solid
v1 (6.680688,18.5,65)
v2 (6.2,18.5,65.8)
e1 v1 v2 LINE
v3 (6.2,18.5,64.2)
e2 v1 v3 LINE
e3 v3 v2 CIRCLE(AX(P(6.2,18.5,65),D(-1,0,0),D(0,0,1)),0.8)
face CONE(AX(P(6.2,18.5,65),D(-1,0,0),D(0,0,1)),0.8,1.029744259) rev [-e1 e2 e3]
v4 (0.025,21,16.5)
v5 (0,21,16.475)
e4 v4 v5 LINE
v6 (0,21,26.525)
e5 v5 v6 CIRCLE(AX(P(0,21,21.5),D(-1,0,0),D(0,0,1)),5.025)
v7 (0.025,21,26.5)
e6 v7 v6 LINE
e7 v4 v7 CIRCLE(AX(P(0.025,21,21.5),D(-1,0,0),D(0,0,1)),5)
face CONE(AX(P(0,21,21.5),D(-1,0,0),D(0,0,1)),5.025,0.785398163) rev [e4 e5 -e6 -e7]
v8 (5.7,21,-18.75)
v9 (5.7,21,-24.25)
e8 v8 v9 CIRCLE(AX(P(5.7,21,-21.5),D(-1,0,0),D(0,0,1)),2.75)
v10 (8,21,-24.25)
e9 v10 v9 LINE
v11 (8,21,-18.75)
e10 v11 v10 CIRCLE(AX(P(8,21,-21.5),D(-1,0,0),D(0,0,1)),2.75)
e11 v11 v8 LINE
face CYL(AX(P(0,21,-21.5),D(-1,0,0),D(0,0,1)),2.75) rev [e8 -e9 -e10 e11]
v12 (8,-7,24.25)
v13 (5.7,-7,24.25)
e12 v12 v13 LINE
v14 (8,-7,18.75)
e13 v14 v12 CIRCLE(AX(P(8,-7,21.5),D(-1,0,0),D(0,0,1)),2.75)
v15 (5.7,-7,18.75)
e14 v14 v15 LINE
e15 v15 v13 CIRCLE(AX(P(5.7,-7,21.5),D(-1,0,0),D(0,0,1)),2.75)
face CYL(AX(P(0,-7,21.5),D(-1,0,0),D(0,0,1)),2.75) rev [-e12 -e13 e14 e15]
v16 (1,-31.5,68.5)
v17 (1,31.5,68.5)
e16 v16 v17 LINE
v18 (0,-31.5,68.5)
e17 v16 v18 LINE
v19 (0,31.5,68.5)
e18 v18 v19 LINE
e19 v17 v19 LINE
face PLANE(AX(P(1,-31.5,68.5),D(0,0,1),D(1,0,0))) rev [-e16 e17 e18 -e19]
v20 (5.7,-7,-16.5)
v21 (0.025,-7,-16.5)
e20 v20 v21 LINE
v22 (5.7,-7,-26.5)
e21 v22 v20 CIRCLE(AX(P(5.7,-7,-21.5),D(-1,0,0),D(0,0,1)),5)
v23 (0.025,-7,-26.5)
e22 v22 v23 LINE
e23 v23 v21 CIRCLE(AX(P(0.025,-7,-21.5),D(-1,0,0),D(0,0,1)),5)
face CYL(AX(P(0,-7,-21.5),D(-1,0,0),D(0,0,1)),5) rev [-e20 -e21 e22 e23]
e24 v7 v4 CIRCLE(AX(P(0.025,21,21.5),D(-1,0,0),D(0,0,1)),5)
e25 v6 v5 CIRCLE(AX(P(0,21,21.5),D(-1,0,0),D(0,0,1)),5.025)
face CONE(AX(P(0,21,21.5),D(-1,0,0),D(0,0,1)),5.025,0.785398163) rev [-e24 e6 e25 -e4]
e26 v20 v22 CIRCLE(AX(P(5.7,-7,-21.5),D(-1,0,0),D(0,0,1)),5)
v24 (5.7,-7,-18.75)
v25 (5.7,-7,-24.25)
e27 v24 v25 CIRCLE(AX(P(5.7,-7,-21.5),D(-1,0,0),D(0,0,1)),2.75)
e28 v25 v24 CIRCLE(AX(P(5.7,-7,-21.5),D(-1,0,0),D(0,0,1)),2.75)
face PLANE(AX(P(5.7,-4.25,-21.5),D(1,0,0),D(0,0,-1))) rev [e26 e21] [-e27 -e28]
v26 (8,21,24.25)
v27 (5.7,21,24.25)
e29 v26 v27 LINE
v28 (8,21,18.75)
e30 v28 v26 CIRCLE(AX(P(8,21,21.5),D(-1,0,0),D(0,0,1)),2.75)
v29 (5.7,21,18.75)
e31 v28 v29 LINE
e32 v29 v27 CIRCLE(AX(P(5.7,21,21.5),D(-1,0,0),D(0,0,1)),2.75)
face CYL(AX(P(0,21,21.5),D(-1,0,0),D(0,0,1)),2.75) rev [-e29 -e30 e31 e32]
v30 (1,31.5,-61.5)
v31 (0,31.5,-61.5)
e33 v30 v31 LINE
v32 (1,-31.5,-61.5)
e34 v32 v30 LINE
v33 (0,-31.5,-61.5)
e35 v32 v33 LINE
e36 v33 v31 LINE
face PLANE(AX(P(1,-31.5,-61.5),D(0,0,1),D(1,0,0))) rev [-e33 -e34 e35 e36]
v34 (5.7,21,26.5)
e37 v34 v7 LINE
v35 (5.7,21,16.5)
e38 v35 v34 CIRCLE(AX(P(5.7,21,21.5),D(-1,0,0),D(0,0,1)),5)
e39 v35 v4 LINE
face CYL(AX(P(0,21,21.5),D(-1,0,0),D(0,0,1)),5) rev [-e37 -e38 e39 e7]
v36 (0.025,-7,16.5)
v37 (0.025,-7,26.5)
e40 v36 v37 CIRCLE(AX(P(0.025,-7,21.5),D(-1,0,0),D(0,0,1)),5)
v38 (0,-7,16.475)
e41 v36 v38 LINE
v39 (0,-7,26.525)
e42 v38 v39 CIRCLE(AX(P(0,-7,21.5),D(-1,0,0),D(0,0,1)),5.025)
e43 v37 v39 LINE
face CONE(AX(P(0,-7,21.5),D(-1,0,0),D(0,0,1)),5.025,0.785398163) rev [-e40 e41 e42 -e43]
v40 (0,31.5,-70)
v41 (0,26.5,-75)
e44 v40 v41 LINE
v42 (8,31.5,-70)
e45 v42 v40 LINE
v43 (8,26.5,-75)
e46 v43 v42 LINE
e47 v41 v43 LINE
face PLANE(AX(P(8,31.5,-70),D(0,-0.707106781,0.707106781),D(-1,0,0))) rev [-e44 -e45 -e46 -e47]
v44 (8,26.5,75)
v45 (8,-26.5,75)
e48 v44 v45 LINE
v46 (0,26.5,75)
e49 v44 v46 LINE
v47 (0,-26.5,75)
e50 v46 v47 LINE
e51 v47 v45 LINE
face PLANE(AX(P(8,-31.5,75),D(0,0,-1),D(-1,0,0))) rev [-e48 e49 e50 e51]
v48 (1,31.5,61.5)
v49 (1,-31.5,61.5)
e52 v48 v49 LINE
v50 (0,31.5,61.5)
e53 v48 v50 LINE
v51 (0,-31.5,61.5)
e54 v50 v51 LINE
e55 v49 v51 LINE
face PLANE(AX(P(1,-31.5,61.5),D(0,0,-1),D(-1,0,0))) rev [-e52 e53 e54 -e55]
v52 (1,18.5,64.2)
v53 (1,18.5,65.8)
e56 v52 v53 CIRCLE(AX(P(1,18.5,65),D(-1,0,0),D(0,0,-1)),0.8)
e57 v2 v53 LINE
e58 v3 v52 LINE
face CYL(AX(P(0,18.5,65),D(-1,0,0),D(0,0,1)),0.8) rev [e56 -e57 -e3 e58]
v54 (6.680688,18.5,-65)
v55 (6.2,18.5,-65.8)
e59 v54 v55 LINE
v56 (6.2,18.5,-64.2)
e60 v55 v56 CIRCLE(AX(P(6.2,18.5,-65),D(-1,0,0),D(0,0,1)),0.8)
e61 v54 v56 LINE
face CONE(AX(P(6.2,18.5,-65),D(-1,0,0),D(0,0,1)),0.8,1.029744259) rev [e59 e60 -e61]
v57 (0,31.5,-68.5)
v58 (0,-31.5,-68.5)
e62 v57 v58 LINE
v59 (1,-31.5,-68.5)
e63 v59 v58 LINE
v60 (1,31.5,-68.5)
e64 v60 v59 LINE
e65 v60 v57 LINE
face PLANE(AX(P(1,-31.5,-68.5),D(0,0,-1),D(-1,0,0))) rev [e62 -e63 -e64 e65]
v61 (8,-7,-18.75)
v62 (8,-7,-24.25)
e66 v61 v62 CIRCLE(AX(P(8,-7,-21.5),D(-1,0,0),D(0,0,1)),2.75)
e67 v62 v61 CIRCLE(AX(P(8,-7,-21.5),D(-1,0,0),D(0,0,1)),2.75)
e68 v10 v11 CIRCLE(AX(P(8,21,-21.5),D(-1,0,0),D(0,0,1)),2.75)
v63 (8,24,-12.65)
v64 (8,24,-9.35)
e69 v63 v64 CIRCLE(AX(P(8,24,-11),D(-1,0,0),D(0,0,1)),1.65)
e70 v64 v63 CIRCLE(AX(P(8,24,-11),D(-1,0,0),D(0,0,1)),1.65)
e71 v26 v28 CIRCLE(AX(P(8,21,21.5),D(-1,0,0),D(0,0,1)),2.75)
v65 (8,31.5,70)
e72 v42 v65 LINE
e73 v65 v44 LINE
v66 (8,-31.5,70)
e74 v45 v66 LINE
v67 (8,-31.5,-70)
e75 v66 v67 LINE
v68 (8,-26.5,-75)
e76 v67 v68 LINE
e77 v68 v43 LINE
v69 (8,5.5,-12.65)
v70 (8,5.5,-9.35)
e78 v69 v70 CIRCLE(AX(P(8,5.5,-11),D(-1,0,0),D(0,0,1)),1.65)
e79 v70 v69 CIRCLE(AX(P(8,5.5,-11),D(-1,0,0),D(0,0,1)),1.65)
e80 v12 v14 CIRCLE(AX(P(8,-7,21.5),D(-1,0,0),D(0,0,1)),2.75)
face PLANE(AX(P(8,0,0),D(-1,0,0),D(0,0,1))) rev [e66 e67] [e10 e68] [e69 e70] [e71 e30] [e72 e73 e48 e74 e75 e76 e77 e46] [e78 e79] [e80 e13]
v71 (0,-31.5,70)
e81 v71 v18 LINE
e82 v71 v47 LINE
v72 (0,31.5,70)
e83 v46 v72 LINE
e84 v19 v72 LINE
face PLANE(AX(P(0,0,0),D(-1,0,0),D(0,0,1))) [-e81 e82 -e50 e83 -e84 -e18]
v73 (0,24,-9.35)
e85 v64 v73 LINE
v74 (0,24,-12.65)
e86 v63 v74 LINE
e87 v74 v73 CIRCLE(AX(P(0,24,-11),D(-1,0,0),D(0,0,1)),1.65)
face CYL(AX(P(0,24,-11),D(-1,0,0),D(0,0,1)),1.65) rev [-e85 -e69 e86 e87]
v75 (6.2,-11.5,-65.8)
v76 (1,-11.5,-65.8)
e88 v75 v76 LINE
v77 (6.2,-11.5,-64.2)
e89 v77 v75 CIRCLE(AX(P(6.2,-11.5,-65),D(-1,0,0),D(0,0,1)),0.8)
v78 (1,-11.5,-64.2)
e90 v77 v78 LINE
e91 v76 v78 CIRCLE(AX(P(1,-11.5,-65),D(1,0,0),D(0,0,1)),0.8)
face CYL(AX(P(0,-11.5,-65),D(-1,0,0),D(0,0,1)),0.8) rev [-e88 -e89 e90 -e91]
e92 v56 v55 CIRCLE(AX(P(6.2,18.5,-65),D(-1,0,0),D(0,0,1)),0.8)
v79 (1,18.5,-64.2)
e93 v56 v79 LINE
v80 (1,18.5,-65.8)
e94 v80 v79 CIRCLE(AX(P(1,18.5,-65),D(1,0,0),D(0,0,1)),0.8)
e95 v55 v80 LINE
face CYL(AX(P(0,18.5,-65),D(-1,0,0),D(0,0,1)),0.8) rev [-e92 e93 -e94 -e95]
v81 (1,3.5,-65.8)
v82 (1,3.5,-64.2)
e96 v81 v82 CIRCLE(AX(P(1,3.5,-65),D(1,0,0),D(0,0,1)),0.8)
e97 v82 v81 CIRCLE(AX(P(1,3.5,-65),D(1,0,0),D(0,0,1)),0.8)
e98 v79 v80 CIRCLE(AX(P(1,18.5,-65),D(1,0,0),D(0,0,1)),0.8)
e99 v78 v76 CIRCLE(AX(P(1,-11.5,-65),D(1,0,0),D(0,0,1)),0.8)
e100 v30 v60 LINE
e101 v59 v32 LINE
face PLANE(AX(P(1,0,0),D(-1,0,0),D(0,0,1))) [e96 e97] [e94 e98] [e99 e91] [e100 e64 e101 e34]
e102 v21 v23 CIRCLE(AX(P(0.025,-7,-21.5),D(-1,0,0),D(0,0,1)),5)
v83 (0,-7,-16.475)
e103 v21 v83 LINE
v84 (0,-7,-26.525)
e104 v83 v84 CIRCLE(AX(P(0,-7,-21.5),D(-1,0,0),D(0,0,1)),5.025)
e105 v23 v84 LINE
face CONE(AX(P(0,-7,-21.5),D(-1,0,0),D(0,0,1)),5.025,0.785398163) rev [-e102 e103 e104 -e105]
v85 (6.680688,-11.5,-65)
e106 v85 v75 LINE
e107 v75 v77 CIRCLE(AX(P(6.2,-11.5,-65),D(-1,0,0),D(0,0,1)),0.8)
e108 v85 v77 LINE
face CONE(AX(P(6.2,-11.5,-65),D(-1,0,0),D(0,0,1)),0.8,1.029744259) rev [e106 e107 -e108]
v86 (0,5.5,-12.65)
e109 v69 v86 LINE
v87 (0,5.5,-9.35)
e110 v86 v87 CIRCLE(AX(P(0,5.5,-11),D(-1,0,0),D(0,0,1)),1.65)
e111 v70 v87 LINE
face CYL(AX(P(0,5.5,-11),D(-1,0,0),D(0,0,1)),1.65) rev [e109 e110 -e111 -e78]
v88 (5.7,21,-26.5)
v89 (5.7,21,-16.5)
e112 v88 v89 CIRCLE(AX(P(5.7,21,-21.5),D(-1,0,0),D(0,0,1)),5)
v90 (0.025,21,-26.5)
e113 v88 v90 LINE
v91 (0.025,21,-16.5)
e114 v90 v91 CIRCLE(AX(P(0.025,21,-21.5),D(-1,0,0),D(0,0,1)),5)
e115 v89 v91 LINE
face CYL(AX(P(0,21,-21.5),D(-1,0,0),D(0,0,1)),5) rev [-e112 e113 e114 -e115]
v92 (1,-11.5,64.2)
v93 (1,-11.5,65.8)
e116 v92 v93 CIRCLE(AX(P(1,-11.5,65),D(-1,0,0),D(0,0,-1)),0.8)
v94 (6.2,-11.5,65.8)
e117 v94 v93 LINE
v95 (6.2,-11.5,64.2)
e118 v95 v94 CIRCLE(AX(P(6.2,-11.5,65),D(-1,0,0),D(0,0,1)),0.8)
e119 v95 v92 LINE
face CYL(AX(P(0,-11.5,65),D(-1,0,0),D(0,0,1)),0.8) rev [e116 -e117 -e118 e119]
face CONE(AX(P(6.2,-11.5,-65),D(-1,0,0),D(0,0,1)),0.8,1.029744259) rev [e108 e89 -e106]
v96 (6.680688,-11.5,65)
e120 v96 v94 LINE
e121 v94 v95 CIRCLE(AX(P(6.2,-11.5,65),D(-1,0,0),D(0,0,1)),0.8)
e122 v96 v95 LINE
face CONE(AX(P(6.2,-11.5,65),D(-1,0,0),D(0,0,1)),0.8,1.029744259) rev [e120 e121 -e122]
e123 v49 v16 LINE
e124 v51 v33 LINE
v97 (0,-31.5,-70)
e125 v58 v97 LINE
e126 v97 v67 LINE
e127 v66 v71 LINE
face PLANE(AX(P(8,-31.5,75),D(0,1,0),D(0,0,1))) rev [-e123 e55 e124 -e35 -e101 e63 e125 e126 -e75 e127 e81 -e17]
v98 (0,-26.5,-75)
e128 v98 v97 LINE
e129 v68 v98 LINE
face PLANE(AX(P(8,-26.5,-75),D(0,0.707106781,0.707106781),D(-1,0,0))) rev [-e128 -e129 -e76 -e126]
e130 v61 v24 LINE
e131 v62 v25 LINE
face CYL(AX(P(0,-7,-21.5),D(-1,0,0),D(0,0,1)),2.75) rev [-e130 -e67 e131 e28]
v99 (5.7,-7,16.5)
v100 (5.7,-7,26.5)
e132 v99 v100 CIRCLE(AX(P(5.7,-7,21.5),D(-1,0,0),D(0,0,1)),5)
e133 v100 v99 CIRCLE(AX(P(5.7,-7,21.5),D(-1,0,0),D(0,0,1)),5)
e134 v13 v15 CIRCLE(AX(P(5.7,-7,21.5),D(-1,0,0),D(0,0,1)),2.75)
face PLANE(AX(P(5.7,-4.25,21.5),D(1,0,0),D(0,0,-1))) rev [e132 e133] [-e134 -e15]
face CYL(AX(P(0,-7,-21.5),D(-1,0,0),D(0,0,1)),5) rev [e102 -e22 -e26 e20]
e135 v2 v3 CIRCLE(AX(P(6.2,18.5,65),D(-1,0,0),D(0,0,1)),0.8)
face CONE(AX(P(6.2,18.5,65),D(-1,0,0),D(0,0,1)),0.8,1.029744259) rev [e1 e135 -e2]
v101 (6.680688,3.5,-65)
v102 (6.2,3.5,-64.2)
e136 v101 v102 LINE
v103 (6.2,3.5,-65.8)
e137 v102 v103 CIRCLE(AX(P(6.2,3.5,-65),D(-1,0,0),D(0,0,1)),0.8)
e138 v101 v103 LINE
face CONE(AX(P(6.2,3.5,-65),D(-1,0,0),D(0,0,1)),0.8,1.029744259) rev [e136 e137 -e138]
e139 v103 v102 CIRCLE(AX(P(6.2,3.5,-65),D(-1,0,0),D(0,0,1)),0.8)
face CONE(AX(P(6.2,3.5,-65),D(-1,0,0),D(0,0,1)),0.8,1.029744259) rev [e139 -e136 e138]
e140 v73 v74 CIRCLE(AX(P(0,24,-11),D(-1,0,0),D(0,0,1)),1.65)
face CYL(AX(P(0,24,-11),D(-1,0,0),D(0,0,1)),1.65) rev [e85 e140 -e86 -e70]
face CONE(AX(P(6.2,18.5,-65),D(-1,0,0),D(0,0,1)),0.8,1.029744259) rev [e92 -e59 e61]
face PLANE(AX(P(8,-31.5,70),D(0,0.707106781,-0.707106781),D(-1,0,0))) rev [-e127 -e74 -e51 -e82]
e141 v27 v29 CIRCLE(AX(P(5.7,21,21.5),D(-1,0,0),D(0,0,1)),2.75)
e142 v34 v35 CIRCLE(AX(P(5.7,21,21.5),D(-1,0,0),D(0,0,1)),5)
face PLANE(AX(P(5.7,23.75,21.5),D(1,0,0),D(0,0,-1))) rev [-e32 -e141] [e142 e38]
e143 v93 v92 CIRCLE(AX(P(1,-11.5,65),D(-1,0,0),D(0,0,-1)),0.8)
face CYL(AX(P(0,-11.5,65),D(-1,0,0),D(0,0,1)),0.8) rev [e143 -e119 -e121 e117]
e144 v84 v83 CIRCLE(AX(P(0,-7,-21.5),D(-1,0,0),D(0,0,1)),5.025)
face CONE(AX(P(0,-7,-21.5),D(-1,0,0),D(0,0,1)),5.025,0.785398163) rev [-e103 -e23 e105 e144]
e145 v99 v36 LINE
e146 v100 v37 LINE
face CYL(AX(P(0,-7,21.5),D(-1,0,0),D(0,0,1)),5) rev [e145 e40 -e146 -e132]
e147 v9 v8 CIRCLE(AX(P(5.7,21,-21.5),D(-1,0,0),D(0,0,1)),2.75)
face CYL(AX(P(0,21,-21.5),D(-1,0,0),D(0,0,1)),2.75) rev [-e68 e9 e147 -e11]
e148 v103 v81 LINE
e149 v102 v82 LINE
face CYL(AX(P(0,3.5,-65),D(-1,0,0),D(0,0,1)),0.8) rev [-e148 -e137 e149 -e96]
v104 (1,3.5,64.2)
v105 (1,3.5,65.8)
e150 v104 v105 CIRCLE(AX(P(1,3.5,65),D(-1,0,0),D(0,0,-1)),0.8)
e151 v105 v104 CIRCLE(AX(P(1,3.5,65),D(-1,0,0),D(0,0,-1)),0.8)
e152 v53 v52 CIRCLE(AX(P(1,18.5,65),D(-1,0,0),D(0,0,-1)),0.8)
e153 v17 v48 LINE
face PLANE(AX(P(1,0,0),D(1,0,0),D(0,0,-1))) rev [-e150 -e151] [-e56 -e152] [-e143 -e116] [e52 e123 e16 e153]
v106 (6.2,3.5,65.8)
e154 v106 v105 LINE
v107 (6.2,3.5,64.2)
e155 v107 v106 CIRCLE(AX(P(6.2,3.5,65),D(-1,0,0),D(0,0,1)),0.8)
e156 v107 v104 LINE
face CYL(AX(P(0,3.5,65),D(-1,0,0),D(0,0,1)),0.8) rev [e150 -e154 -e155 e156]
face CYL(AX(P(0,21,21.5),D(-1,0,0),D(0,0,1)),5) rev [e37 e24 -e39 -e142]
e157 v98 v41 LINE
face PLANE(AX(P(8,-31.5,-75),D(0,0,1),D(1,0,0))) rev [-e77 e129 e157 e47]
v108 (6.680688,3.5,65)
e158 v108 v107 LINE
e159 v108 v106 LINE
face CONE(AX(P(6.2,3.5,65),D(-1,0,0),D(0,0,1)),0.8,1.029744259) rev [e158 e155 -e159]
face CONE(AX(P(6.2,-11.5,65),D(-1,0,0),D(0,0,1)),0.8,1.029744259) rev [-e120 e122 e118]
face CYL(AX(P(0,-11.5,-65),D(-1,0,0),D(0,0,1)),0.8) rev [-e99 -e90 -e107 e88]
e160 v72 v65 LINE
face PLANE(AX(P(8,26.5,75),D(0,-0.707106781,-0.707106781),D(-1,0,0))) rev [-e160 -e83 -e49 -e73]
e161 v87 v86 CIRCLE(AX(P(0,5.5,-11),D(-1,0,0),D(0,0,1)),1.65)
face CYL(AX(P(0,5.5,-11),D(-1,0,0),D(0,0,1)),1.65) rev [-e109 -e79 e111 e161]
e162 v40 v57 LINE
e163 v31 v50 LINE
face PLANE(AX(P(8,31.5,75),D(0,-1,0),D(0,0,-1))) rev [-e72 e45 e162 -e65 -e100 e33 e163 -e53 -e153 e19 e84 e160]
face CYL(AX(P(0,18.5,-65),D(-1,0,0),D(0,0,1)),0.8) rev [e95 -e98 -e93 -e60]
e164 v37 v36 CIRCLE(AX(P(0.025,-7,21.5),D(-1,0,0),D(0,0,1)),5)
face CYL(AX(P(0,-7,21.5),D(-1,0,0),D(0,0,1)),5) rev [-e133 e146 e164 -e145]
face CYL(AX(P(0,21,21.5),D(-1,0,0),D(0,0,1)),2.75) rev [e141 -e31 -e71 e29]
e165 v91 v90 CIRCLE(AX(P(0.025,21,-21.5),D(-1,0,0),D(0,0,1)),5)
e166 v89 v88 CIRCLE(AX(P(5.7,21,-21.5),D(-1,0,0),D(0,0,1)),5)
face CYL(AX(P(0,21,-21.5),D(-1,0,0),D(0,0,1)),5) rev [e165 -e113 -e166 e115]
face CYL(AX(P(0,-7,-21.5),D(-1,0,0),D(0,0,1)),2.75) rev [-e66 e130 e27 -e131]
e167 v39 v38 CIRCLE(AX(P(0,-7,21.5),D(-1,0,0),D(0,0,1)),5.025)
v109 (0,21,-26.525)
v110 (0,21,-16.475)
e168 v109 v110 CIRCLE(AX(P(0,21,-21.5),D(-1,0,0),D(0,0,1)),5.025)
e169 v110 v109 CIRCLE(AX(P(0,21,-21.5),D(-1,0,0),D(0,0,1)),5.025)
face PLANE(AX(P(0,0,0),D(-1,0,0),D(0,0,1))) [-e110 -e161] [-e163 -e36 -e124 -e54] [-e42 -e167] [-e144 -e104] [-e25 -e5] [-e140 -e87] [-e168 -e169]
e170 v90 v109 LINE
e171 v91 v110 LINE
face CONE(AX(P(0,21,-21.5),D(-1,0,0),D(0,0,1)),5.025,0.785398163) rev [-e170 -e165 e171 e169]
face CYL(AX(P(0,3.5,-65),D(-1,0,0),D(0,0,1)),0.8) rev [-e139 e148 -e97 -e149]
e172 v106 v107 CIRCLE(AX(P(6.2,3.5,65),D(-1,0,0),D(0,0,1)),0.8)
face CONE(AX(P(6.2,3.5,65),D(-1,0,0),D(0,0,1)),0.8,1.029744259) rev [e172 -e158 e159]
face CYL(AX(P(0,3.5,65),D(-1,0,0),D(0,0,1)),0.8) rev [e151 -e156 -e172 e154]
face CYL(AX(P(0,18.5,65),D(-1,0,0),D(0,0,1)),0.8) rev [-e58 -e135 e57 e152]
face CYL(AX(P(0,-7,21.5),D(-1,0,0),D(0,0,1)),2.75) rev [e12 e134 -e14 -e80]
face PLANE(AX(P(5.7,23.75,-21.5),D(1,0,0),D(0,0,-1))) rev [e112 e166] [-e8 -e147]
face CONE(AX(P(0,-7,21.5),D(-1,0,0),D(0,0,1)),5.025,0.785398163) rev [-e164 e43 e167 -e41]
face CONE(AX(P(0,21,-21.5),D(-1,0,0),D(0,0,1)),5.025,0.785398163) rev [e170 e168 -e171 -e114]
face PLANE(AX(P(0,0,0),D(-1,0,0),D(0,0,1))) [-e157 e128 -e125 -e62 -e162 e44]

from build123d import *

# Parameters (mm, degrees)
SKETCH1_W                                    = 150
SKETCH1_H                                    = 63
BOSS_EXTRUDE1_DEPTH                          = 8
M4_TAPPED_HOLE1_D                            = 3.3
M4_TAPPED_HOLE1_DEPTH                        = 10.1
M4_TAPPED_HOLE1_TIP                          = 0.991420021
CBORE_FOR_M5_HEXAGON_SOCKET_HEAD_CAP_2_COUNT = 2
CBORE_FOR_M5_HEXAGON_SOCKET_HEAD_CAP_2_PITCH = 28
CBORE_FOR_M5_HEXAGON_SOCKET_HEAD_CAP_3_COUNT = 2
CBORE_FOR_M5_HEXAGON_SOCKET_HEAD_CAP_3_PITCH = 43
CBORE_FOR_M5_HEXAGON_SOCKET_HEAD_CAP_4_COUNT = 2
CBORE_FOR_M5_HEXAGON_SOCKET_HEAD_CAP_4_PITCH = 51.312766443
M2_TAPPED_HOLE1_D                            = 1.6
M2_TAPPED_HOLE1_DEPTH                        = 6.2
M2_TAPPED_HOLE1_TIP                          = 0.480688495
SKETCH17_W                                   = 7
SKETCH17_H                                   = 63
CUT_EXTRUDE1_DEPTH                           = 1
CHAMFER1_SIZE                                = 5


with BuildPart() as part:
    # Sketch1 → Boss-Extrude1 (new body)
    with BuildSketch(Plane(origin=(0, 0, 0), x_dir=(0, 0, -1), z_dir=(1, 0, 0))):
        Rectangle(SKETCH1_W, SKETCH1_H)
    extrude(amount=BOSS_EXTRUDE1_DEPTH)

    # M4 Tapped Hole1
    with Locations(Plane.ZY):
        with Locations((-11, 24), (-11, 5.5)):
            Hole(M4_TAPPED_HOLE1_D / 2, depth=M4_TAPPED_HOLE1_DEPTH)
            with Locations((0, 0, -(M4_TAPPED_HOLE1_DEPTH + M4_TAPPED_HOLE1_TIP / 2))):  # 118° drill point
                Cone(0, M4_TAPPED_HOLE1_D / 2, M4_TAPPED_HOLE1_TIP, mode=Mode.SUBTRACT)

    # Sketch15 → CBORE for M5 Hexagon socket head cap screws1 (revolve, cut)
    with BuildSketch(Plane(origin=(0, 21, 21.5), x_dir=(0, 0, 1), z_dir=(0, 1, 0))):
        Polygon((0, 0), (0, 14.052366702), (2.75, 12.4), (2.75, 5.7), (5, 5.7), (5, 0.025), (5.025, 0), align=None)
    cbore_for_m5_hexagon_socket_head_cap_scr = revolve(axis=Axis((-6.35, 21, 21.5), (1, 0, 0)), mode=Mode.SUBTRACT)

    # CBORE for M5 Hexagon socket head cap 2: CBORE for M5 Hexagon socket head cap screws1 ×2
    with Locations(*[(0, -i * CBORE_FOR_M5_HEXAGON_SOCKET_HEAD_CAP_2_PITCH, 0) for i in range(1, CBORE_FOR_M5_HEXAGON_SOCKET_HEAD_CAP_2_COUNT)]):
        add(cbore_for_m5_hexagon_socket_head_cap_scr, mode=Mode.SUBTRACT)

    # CBORE for M5 Hexagon socket head cap 3: CBORE for M5 Hexagon socket head cap screws1 ×2
    with Locations(*[(0, 0, -i * CBORE_FOR_M5_HEXAGON_SOCKET_HEAD_CAP_3_PITCH) for i in range(1, CBORE_FOR_M5_HEXAGON_SOCKET_HEAD_CAP_3_COUNT)]):
        add(cbore_for_m5_hexagon_socket_head_cap_scr, mode=Mode.SUBTRACT)

    # CBORE for M5 Hexagon socket head cap 4: CBORE for M5 Hexagon socket head cap screws1 ×2
    with Locations(*[Vector(0, -0.5456731714374324, -0.8379980847074858) * (i * CBORE_FOR_M5_HEXAGON_SOCKET_HEAD_CAP_4_PITCH) for i in range(1, CBORE_FOR_M5_HEXAGON_SOCKET_HEAD_CAP_4_COUNT)]):
        add(cbore_for_m5_hexagon_socket_head_cap_scr, mode=Mode.SUBTRACT)

    # M2 Tapped Hole1
    with Locations(Plane.ZY):
        with Locations((-65, 18.5), (-65, 3.5), (-65, -11.5), (65, -11.5), (65, 3.5), (65, 18.5)):
            Hole(M2_TAPPED_HOLE1_D / 2, depth=M2_TAPPED_HOLE1_DEPTH)
            with Locations((0, 0, -(M2_TAPPED_HOLE1_DEPTH + M2_TAPPED_HOLE1_TIP / 2))):  # 118° drill point
                Cone(0, M2_TAPPED_HOLE1_D / 2, M2_TAPPED_HOLE1_TIP, mode=Mode.SUBTRACT)

    # Sketch17 → Cut-Extrude1 (cut)
    with BuildSketch(Plane.ZY):
        with Locations((65, 0)):
            Rectangle(SKETCH17_W, SKETCH17_H)
        with Locations((-65, 0)):
            Rectangle(SKETCH17_W, SKETCH17_H)
    extrude(amount=-CUT_EXTRUDE1_DEPTH, mode=Mode.SUBTRACT)

    # Chamfer1
    chamfer1_edges = [part.edges().sort_by_distance(p)[0] for p in [
        (4, -31.5, -75),
        (4, -31.5, 75),
        (4, 31.5, 75),
        (4, 31.5, -75),
    ]]
    chamfer(chamfer1_edges, length=CHAMFER1_SIZE)


solid = part.part
